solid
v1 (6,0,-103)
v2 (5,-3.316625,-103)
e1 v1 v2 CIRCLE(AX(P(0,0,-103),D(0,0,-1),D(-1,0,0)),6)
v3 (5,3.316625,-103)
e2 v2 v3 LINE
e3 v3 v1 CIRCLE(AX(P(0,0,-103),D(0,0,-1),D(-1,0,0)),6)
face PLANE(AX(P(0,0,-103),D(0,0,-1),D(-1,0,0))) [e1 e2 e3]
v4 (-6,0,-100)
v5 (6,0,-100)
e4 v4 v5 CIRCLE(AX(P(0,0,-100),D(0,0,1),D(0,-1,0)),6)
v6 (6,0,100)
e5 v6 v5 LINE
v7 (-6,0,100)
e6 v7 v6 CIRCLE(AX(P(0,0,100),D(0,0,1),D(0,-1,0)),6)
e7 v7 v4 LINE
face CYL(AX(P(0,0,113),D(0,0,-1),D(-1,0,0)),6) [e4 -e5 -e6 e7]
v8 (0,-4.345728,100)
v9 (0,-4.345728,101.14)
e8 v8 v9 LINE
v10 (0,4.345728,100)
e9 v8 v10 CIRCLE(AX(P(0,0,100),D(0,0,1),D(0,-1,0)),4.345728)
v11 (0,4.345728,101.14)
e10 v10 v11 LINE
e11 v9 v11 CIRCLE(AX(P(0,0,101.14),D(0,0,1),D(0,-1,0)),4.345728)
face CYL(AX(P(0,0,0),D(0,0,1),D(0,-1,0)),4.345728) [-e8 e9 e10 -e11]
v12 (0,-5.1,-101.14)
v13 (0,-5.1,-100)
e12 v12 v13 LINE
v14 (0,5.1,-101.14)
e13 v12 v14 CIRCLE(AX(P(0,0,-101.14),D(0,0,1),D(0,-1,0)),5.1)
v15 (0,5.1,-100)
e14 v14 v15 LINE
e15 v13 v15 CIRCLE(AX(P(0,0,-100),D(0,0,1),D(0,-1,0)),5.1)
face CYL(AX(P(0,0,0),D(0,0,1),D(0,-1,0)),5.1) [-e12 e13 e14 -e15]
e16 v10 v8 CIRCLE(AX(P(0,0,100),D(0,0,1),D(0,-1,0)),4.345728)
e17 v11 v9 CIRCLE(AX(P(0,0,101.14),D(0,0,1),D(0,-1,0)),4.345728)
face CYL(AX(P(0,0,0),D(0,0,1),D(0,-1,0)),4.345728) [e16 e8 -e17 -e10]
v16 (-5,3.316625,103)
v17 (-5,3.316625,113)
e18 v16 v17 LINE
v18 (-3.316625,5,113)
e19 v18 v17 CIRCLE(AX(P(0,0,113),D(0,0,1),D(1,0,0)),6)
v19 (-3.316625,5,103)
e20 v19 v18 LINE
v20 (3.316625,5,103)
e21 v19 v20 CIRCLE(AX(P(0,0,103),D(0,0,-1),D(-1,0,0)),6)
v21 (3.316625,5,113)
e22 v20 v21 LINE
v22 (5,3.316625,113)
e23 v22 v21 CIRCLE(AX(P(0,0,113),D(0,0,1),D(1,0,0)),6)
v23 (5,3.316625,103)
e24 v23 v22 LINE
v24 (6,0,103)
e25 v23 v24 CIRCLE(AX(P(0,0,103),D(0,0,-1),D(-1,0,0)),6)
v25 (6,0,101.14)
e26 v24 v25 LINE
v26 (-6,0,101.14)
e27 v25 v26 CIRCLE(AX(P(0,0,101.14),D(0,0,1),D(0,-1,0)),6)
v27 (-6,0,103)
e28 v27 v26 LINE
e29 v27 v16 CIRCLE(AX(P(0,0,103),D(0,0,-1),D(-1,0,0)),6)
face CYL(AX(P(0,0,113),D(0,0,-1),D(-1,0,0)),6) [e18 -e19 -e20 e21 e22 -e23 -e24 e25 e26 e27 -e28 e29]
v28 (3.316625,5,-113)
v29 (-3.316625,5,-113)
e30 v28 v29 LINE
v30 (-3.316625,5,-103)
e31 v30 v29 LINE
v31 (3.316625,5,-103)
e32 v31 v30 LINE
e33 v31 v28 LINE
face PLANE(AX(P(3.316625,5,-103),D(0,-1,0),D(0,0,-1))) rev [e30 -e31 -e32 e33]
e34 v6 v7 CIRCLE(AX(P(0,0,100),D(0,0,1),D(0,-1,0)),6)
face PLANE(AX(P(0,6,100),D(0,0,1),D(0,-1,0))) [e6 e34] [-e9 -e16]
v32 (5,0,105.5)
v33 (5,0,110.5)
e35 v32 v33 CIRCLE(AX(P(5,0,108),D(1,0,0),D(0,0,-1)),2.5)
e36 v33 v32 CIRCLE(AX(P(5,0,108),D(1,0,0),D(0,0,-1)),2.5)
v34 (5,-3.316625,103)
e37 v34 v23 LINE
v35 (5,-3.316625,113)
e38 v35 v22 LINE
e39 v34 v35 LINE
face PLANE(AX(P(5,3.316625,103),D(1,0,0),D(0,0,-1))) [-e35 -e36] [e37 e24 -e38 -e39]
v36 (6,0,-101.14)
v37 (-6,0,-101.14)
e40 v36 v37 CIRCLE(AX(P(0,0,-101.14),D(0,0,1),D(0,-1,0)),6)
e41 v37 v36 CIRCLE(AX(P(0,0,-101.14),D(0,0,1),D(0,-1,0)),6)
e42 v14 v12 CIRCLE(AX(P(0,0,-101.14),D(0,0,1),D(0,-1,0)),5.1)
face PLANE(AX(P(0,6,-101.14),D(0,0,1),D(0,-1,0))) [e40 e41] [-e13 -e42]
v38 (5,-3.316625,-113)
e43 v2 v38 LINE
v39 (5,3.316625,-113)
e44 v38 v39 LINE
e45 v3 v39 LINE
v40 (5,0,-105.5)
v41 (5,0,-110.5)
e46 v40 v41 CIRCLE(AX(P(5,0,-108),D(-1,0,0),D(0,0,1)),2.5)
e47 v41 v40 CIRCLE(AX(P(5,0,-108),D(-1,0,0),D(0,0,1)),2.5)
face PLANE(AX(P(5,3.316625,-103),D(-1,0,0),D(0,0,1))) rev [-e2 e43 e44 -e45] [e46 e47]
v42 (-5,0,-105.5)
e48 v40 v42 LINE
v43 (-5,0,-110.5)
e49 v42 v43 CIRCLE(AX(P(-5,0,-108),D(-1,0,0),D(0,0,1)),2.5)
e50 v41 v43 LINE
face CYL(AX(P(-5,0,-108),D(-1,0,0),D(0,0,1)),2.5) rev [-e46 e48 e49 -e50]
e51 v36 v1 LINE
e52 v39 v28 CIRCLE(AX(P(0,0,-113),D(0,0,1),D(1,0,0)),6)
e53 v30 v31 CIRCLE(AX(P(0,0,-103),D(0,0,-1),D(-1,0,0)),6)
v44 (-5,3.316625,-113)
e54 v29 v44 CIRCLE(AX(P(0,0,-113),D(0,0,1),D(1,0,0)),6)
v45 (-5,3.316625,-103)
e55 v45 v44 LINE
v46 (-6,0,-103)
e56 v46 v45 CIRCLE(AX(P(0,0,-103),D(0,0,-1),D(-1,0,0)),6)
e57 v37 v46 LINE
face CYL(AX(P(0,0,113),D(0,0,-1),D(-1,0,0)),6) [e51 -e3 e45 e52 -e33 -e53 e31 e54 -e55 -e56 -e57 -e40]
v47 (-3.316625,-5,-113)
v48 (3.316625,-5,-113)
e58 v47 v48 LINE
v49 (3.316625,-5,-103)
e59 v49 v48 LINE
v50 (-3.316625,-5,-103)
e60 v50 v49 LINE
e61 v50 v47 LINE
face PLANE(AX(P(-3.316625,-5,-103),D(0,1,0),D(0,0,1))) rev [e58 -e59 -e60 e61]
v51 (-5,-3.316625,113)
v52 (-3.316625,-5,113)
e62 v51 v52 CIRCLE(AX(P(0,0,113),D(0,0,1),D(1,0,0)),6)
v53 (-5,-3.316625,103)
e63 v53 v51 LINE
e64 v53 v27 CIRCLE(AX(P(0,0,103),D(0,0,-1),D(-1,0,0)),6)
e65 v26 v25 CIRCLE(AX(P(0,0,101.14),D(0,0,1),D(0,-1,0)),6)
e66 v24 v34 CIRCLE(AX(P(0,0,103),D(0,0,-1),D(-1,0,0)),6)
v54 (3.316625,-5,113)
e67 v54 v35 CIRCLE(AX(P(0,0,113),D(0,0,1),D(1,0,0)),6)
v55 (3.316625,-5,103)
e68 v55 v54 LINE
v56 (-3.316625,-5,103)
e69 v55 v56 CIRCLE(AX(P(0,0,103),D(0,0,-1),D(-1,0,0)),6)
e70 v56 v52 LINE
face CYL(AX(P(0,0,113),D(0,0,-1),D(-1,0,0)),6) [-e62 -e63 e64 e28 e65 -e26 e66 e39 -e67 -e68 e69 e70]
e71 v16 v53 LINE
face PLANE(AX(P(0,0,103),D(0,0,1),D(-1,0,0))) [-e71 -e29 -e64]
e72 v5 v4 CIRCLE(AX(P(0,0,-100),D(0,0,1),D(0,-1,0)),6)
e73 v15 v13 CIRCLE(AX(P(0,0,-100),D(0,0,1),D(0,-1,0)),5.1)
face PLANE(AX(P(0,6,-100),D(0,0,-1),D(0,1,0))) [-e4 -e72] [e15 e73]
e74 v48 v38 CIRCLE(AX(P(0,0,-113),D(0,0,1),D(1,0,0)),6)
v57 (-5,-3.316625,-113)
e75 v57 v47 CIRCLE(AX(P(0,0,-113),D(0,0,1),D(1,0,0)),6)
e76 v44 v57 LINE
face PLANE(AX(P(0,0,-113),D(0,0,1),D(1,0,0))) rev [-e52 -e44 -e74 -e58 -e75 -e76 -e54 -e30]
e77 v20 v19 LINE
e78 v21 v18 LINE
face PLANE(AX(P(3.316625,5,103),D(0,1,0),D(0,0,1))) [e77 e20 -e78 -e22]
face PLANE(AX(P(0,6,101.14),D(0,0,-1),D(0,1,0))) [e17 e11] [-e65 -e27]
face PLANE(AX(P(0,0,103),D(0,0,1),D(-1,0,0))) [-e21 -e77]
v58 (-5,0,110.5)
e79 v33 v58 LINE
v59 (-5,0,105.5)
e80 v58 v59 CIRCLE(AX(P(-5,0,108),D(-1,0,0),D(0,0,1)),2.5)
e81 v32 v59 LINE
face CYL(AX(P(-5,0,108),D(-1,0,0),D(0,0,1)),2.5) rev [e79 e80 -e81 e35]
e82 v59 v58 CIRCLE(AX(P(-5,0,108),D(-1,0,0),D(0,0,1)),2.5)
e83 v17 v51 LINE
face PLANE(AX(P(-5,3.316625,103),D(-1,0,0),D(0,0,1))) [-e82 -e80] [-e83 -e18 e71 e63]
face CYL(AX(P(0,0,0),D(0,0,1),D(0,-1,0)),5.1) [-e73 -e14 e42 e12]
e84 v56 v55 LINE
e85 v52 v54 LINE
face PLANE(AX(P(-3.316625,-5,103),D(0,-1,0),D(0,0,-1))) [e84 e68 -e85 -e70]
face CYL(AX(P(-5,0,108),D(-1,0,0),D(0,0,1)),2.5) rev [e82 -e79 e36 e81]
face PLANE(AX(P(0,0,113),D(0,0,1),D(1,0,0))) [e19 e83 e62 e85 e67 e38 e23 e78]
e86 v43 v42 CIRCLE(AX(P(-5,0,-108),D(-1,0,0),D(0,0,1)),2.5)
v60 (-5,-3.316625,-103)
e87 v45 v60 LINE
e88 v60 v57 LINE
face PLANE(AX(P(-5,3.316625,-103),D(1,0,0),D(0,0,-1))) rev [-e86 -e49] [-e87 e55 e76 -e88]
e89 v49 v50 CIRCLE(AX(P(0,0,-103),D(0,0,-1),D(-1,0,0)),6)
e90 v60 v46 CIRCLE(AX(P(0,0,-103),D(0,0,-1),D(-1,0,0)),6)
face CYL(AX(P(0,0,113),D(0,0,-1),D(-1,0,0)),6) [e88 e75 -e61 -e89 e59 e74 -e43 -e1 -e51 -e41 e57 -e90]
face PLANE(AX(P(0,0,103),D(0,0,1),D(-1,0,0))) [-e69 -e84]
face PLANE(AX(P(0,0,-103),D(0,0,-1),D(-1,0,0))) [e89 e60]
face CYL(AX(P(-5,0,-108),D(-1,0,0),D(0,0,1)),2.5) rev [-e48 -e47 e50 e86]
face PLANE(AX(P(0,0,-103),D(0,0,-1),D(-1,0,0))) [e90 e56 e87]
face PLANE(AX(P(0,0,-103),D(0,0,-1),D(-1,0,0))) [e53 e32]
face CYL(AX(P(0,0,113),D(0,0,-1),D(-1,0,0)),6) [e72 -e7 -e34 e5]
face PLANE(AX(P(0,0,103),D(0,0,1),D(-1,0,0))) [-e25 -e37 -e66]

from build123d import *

# Parameters (mm, degrees)
SKETCH_1_R          = 6
EXTRUDE_1_DEPTH     = 113
SKETCH_2_W          = 1.14
SKETCH_2_H          = 0.9
SKETCH_2_H_2        = 1.654271951
CUT_EXTRUDE_START   = -10
CUT_EXTRUDE_1_DEPTH = 10
HOLE_WIZARD_M6_1_D  = 5


with BuildPart() as part:
    # 草图1 → 凸台-拉伸1 (new, symmetric)
    with BuildSketch(Plane.XY):
        Circle(SKETCH_1_R)
    extrude(amount=EXTRUDE_1_DEPTH, both=True)

    # 草图2 → 切除-旋转1 (revolve, cut)
    with BuildSketch(Plane(origin=(0, 0, 0), x_dir=(0, 0, -1), z_dir=(1, 0, 0)), mode=Mode.PRIVATE) as cut_revolve_1_sk:
        with Locations((100.57, 5.55)):
            Rectangle(SKETCH_2_W, SKETCH_2_H)
        with Locations((-100.57, 5.172864024)):
            Rectangle(SKETCH_2_W, SKETCH_2_H_2)
    revolve(cut_revolve_1_sk.sketch.rotate(Axis((0, 0, 0), (0, 0, -1)), 180), axis=Axis((0, 0, 0), (0, 0, -1)), mode=Mode.SUBTRACT)

    # 草图3 → 切除-拉伸1 (cut)
    with BuildSketch(Plane(origin=(0, 0, -113), x_dir=(-1, 0, 0), z_dir=(0, 0, -1)).offset(CUT_EXTRUDE_START)):
        with BuildLine():
            Line((-5, 3.31662479), (-5, -3.31662479))
            ThreePointArc((-5, -3.31662479), (-6, 0), (-5, 3.31662479))
        make_face()
        with BuildLine():
            Line((5, 3.31662479), (5, -3.31662479))
            ThreePointArc((5, -3.31662479), (6, 0), (5, 3.31662479))
        make_face()
        with BuildLine():
            Line((-3.31662479, 5), (3.31662479, 5))
            ThreePointArc((3.31662479, 5), (0, 6), (-3.31662479, 5))
        make_face()
        with BuildLine():
            Line((3.31662479, -5), (-3.31662479, -5))
            ThreePointArc((-3.31662479, -5), (0, -6), (3.31662479, -5))
        make_face()
    cut_extrude_1 = extrude(amount=CUT_EXTRUDE_1_DEPTH, mode=Mode.SUBTRACT)

    # M6 螺纹孔1 (through all)
    with Locations(Plane.ZY.offset(5)):
        with Locations((-108, 0)):
            hole_wizard_m6_1 = Hole(HOLE_WIZARD_M6_1_D / 2)

    # 镜向1: 切除-拉伸1, M6 螺纹孔1 across plane
    add(cut_extrude_1.mirror(Plane.XY), mode=Mode.SUBTRACT)
    add(hole_wizard_m6_1.mirror(Plane.XY), mode=Mode.SUBTRACT)


solid = part.part
